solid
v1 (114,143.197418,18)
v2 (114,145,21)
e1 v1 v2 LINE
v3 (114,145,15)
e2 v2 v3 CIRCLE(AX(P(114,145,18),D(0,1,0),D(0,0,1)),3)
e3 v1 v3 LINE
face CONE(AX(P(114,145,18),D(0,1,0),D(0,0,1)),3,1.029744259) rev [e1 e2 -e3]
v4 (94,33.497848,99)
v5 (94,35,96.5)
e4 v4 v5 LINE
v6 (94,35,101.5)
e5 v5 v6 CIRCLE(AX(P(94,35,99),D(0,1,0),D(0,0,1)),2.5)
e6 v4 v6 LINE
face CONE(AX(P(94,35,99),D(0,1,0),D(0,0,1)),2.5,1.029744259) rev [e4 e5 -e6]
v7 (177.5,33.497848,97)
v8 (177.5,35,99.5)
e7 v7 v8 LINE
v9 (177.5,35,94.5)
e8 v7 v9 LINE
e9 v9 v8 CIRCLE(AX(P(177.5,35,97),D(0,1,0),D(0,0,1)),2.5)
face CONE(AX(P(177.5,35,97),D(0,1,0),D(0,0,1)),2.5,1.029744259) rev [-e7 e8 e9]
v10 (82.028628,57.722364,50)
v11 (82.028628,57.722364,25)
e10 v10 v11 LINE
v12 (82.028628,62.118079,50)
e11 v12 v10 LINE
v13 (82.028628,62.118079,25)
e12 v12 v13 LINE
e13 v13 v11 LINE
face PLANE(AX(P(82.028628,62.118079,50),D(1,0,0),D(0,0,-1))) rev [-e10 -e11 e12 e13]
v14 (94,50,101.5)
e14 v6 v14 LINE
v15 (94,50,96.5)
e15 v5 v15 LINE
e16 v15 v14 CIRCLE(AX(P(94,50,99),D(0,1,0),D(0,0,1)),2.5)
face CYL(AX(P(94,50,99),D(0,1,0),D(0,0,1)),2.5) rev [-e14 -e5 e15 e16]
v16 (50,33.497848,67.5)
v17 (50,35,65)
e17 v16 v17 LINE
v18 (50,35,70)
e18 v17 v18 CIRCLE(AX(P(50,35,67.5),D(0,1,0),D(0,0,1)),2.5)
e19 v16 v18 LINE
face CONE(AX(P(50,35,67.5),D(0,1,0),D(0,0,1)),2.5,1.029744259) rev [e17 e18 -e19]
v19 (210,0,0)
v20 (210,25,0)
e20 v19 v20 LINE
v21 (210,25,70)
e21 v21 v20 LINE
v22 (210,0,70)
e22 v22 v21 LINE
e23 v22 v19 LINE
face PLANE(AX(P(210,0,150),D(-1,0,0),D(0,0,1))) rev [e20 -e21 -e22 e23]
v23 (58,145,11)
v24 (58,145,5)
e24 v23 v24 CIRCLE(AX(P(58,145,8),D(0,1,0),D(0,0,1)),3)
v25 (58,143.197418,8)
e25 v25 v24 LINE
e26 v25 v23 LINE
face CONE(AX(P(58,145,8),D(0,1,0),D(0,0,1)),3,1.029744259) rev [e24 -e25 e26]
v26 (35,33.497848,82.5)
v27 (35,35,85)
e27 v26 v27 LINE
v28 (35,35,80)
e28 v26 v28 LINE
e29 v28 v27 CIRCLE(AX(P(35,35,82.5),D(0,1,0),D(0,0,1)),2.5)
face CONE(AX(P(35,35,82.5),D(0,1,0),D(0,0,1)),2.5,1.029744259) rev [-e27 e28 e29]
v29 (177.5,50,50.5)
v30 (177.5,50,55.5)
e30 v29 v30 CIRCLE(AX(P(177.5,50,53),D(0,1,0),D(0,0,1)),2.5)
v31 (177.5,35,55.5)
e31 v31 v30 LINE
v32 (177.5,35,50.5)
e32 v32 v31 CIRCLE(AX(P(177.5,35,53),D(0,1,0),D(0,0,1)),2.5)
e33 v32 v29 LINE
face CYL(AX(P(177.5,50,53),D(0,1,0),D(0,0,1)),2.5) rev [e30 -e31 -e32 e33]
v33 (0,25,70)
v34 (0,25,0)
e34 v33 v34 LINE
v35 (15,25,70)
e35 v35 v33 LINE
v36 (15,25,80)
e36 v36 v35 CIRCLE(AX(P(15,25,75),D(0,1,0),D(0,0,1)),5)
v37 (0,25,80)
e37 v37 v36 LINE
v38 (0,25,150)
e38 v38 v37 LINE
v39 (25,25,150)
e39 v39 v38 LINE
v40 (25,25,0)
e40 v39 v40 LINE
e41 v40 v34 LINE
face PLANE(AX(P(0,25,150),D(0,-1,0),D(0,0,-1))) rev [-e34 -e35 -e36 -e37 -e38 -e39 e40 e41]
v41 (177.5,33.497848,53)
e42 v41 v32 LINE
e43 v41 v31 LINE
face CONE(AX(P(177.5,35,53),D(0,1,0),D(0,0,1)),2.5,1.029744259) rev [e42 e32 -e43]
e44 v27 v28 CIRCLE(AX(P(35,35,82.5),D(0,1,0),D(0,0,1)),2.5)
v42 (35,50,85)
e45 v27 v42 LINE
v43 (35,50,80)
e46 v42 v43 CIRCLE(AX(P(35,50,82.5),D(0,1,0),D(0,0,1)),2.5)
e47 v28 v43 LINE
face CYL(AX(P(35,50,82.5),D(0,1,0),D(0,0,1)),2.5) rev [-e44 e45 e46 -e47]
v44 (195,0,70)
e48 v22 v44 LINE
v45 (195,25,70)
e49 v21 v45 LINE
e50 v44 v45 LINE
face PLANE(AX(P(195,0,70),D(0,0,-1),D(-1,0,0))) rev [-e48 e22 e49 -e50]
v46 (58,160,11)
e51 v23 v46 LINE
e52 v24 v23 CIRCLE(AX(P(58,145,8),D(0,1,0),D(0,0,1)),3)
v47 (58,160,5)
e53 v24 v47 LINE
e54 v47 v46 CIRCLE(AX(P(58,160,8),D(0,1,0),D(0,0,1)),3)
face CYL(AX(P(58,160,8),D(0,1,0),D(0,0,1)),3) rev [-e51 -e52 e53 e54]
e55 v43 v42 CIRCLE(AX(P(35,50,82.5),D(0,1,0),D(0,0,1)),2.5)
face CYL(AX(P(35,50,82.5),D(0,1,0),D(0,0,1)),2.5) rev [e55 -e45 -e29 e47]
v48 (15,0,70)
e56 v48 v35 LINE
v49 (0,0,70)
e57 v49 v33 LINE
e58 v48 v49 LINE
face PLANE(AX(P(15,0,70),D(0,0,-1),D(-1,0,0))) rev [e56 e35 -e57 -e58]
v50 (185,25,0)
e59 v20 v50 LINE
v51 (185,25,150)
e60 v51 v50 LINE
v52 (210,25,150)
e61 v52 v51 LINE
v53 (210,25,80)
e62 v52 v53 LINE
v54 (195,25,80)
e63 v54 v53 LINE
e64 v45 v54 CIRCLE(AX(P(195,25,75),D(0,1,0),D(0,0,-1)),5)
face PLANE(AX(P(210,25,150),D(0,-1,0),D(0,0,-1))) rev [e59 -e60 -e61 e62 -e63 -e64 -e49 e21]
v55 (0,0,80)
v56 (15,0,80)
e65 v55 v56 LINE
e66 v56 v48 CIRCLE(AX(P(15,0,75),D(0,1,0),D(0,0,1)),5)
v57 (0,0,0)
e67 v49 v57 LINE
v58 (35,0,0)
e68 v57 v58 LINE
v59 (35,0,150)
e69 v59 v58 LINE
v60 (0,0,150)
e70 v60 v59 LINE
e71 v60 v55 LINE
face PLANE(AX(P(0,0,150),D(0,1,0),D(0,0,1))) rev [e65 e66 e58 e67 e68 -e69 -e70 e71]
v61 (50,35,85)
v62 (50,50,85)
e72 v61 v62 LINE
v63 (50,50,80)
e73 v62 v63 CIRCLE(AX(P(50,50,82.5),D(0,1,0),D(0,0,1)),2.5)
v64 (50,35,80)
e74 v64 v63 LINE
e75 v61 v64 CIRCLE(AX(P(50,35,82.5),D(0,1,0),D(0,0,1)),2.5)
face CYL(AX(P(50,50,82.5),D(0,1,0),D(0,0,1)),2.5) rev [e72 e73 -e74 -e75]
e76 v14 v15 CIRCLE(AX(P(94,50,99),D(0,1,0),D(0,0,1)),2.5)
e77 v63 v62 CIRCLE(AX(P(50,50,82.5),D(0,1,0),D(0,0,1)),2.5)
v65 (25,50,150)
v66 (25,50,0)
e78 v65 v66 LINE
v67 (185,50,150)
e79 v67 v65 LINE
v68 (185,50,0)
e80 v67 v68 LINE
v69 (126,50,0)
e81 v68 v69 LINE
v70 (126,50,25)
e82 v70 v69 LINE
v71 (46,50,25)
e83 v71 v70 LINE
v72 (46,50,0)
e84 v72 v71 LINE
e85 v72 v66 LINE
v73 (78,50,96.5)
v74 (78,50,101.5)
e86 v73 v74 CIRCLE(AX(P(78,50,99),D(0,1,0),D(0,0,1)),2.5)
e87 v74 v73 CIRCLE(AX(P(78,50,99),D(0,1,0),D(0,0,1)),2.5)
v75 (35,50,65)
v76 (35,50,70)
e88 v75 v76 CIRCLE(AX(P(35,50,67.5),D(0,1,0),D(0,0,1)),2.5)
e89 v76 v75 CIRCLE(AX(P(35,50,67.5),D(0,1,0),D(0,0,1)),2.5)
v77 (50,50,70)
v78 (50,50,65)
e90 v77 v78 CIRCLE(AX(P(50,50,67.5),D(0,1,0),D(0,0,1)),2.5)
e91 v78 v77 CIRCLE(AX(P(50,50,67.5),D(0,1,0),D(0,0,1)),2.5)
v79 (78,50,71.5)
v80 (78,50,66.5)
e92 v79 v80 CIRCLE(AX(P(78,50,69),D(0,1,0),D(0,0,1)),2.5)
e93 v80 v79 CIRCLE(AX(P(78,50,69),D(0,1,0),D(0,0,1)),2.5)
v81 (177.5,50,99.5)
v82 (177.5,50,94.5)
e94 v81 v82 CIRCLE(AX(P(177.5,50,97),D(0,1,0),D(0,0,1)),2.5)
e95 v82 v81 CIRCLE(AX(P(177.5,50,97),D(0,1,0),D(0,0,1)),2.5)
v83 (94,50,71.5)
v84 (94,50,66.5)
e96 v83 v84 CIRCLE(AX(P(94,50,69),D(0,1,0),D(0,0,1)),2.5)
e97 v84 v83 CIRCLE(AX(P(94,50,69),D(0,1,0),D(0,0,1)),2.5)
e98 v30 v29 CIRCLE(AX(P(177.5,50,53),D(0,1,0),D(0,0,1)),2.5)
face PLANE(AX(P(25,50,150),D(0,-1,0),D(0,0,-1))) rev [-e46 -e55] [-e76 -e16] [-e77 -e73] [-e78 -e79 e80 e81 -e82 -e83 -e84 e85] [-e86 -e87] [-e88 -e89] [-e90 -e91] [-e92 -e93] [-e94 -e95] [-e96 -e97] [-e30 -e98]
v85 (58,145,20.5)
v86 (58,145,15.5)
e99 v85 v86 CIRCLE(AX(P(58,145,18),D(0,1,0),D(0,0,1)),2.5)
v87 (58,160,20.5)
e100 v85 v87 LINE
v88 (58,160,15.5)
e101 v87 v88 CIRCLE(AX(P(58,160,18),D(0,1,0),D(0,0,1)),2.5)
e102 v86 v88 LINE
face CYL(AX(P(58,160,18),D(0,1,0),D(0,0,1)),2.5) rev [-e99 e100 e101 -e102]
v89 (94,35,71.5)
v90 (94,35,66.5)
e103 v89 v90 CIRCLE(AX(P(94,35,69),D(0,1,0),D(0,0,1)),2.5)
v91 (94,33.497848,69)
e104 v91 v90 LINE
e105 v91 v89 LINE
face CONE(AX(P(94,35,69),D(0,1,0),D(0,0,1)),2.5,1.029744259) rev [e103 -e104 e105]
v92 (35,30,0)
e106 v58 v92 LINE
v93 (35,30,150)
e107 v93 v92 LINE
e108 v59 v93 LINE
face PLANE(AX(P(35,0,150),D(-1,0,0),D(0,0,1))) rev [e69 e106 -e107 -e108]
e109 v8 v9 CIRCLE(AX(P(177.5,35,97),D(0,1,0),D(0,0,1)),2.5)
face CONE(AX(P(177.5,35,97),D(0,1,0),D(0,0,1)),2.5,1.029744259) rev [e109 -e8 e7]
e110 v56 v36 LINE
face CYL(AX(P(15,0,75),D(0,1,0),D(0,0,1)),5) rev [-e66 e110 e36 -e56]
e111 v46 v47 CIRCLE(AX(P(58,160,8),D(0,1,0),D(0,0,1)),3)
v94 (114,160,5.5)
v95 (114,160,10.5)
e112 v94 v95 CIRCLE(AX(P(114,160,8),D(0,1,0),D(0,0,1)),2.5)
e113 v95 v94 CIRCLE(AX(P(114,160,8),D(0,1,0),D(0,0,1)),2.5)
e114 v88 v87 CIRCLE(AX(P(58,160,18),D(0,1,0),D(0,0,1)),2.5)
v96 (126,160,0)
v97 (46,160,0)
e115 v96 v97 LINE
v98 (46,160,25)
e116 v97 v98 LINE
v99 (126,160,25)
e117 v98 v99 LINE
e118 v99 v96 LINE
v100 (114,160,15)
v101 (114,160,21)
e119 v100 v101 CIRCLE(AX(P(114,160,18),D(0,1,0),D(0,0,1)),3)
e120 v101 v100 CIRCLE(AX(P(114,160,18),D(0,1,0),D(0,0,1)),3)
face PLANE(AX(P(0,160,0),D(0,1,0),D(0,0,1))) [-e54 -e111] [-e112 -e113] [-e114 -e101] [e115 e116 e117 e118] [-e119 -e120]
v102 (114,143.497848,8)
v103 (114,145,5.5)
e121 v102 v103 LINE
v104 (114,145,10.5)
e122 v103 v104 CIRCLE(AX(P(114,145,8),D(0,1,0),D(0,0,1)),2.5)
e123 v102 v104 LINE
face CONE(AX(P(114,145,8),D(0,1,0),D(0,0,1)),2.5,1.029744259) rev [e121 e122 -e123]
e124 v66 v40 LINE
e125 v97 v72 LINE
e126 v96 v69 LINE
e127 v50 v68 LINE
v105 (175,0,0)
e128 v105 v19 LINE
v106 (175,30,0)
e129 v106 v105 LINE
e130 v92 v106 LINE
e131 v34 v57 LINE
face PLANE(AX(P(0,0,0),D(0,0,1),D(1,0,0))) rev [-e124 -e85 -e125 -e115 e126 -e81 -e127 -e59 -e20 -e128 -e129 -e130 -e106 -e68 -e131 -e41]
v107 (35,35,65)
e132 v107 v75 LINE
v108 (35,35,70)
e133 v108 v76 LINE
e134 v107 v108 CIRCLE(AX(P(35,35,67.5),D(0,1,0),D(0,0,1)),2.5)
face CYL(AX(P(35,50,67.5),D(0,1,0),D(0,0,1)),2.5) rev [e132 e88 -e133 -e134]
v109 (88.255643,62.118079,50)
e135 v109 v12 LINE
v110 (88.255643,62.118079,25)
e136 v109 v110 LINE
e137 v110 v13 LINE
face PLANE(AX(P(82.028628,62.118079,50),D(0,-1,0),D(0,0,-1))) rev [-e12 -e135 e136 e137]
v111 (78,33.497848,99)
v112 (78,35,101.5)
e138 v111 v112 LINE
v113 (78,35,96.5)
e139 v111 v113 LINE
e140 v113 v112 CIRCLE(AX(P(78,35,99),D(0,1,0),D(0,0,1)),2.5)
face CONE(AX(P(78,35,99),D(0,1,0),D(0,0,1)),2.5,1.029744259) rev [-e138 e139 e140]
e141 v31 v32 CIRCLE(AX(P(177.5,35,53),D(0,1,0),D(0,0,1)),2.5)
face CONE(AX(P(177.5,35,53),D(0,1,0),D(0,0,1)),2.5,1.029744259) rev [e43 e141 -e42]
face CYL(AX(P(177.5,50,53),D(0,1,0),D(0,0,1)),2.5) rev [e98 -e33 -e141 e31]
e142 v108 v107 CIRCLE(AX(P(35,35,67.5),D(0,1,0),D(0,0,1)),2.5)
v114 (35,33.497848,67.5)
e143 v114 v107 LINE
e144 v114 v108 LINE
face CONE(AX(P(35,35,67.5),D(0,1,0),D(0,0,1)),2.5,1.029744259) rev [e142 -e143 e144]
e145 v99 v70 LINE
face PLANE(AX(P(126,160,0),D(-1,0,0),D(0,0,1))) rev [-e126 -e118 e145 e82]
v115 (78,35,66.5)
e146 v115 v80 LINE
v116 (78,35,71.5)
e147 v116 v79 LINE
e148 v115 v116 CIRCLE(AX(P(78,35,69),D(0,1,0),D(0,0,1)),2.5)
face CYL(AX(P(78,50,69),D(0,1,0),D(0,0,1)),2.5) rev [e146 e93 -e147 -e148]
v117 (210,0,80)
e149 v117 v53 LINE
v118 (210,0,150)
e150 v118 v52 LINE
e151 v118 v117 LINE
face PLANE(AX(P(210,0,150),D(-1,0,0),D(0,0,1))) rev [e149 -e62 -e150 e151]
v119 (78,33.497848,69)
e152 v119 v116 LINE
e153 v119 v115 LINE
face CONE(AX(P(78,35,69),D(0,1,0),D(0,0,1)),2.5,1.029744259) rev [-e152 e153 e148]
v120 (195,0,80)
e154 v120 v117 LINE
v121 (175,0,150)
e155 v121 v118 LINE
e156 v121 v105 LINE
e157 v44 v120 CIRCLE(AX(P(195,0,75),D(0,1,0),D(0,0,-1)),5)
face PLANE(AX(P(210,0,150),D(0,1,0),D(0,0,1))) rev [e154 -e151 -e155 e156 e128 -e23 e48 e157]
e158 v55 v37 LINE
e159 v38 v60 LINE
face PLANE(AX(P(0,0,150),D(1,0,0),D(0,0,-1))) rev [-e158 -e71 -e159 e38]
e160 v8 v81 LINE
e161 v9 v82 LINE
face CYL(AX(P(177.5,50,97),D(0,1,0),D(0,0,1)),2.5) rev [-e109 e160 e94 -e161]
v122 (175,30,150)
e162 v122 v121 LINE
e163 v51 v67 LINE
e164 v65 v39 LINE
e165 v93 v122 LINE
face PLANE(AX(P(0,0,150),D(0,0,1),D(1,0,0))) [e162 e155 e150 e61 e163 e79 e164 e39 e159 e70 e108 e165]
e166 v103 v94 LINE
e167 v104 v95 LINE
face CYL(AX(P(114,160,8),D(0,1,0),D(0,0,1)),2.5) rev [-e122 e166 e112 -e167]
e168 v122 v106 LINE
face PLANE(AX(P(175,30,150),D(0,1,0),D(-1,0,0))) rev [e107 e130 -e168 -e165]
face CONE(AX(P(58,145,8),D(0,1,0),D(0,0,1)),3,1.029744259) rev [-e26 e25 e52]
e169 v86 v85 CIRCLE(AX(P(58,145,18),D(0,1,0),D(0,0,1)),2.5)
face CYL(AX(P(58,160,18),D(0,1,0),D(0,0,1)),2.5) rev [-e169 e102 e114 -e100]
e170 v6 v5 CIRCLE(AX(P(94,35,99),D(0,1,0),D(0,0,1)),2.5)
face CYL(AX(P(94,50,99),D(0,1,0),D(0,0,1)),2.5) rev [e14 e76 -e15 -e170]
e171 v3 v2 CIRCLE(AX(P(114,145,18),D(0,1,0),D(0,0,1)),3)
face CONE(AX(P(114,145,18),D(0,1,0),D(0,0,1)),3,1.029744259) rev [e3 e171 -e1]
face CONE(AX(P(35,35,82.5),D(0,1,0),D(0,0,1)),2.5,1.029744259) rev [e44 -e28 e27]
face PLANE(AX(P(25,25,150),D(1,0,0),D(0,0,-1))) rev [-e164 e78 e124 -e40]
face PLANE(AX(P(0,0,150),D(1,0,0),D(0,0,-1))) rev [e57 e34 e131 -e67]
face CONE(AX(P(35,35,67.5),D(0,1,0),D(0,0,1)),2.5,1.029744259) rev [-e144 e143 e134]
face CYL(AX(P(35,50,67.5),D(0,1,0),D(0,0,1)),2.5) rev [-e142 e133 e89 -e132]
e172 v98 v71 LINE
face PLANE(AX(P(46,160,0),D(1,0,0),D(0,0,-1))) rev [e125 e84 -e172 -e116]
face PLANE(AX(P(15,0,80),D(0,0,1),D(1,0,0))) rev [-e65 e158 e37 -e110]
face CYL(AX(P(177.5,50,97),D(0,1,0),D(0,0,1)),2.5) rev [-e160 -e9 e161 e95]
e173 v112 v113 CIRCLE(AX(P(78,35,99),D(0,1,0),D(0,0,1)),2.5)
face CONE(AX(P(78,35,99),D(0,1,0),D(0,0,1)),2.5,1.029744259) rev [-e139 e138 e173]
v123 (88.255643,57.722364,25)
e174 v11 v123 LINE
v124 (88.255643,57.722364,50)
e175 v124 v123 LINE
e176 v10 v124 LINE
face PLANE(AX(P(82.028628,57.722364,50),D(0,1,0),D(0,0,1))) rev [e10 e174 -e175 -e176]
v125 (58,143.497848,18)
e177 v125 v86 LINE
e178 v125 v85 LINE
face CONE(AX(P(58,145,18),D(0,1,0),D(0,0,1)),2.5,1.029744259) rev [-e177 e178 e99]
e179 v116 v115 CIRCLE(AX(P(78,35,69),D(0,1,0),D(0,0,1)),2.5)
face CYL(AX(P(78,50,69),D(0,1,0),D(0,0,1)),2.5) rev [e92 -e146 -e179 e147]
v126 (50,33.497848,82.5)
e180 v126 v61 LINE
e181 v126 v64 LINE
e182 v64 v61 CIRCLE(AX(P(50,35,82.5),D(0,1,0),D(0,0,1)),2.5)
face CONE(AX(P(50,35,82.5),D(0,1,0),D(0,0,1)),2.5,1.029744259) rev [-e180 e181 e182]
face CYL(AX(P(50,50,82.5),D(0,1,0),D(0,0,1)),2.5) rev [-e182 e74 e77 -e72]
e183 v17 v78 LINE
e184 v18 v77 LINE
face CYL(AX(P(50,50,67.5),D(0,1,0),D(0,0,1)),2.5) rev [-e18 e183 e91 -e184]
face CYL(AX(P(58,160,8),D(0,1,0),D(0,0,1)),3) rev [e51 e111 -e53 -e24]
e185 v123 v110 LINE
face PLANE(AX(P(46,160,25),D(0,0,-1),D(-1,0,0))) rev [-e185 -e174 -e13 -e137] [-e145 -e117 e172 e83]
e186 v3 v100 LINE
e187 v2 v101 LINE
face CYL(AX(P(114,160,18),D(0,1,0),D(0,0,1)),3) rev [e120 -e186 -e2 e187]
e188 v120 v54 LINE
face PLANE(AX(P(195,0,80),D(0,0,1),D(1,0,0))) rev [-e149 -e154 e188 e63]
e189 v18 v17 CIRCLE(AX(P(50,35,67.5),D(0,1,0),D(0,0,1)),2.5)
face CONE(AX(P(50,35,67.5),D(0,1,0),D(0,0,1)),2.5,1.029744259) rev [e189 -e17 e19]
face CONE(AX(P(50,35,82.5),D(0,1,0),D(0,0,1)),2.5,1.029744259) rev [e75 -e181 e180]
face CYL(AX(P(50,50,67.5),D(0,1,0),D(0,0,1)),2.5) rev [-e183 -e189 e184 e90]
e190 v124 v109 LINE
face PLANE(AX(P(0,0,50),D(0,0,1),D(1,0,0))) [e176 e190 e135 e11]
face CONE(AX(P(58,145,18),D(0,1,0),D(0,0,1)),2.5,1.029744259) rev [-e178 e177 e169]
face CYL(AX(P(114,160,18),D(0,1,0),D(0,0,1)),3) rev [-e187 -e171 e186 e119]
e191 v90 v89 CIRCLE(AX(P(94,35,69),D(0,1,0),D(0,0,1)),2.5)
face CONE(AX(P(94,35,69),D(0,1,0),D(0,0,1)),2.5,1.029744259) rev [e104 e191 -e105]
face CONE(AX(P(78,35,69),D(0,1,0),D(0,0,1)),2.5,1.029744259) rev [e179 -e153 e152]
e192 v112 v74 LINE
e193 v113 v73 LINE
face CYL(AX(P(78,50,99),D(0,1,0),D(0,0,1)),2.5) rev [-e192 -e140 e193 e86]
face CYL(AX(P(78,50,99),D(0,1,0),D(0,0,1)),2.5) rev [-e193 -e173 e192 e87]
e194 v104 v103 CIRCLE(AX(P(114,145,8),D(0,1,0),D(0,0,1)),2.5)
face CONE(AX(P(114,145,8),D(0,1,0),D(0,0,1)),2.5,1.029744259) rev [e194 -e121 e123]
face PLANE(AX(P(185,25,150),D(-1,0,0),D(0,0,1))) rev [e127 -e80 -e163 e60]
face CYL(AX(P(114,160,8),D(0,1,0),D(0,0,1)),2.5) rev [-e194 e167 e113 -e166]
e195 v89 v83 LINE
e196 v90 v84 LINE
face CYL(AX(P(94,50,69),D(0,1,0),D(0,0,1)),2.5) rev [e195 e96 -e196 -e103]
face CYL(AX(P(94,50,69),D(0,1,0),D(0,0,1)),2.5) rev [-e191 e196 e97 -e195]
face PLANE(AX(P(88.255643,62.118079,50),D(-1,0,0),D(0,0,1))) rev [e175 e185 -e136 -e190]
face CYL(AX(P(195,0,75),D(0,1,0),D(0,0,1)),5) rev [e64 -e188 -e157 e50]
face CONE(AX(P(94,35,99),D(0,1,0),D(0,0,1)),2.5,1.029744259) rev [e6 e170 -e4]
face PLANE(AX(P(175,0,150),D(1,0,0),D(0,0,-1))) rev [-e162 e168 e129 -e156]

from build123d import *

# Parameters (mm, degrees)
BOSS_EXTRUDE1_DEPTH        = 150
CUT_EXTRUDE1_DEPTH         = 260.277843249
M6_TAPPED_HOLE1_D          = 5
M6_TAPPED_HOLE1_DEPTH      = 15
M6_TAPPED_HOLE1_TIP        = 1.502151548
SKETCH13_W                 = 80
SKETCH13_H                 = 25
BOSS_EXTRUDE2_DEPTH        = 110
M6_TAPPED_HOLE2_D          = 5
M6_TAPPED_HOLE2_DEPTH      = 15
M6_TAPPED_HOLE2_TIP        = 1.502151548
F_6_0MM_DOWEL_HOLE_1_D     = 6
F_6_0MM_DOWEL_HOLE_1_DEPTH = 15
F_6_0MM_DOWEL_HOLE_1_TIP   = 1.802581857
SKETCH20_W                 = 6.227014718
SKETCH20_H                 = 4.395715082
BOSS_EXTRUDE3_DEPTH        = 25


with BuildPart() as part:
    # Sketch1 → Boss-Extrude1 (new body)
    with BuildSketch(Plane.XY):
        Polygon((0, 0), (0, 25), (25, 25), (25, 50), (185, 50), (185, 25), (210, 25), (210, 0), (175, 0), (175, 30), (35, 30), (35, 0), align=None)
    extrude(amount=BOSS_EXTRUDE1_DEPTH)

    # Sketch9 → Cut-Extrude1 (cut, through all)
    with BuildSketch(Plane(origin=(0, 25, 0), x_dir=(1, 0, 0), z_dir=(0, 1, 0))):
        with BuildLine():
            Line((210, -70), (210, -80))
            Line((210, -80), (195, -80))
            ThreePointArc((195, -80), (190, -75), (195, -70))
            Line((195, -70), (210, -70))
        make_face()
        with BuildLine():
            Line((15, -70), (0, -70))
            Line((0, -70), (0, -80))
            Line((0, -80), (15, -80))
            ThreePointArc((15, -80), (20, -75), (15, -70))
        make_face()
    extrude(amount=-CUT_EXTRUDE1_DEPTH, mode=Mode.SUBTRACT)

    # M6 Tapped Hole1
    with Locations(Plane(origin=(0, 50, 0), x_dir=(1, 0, 0), z_dir=(0, 1, 0))):
        with Locations((35, -82.5), (35, -67.5), (50, -67.5), (50, -82.5), (78, -69), (78, -99), (94, -69), (94, -99), (177.5, -97), (177.5, -53)):
            Hole(M6_TAPPED_HOLE1_D / 2, depth=M6_TAPPED_HOLE1_DEPTH)
            with Locations((0, 0, -(M6_TAPPED_HOLE1_DEPTH + M6_TAPPED_HOLE1_TIP / 2))):  # 118° drill point
                Cone(0, M6_TAPPED_HOLE1_D / 2, M6_TAPPED_HOLE1_TIP, mode=Mode.SUBTRACT)

    # Sketch13 → Boss-Extrude2 (add)
    with BuildSketch(Plane(origin=(0, 50, 0), x_dir=(1, 0, 0), z_dir=(0, 1, 0))):
        with Locations((86, -12.5)):
            Rectangle(SKETCH13_W, SKETCH13_H)
    extrude(amount=BOSS_EXTRUDE2_DEPTH)

    # M6 Tapped Hole2
    with Locations(Plane(origin=(0, 160, 0), x_dir=(1, 0, 0), z_dir=(0, 1, 0))):
        with Locations((58, -18), (114, -8)):
            Hole(M6_TAPPED_HOLE2_D / 2, depth=M6_TAPPED_HOLE2_DEPTH)
            with Locations((0, 0, -(M6_TAPPED_HOLE2_DEPTH + M6_TAPPED_HOLE2_TIP / 2))):  # 118° drill point
                Cone(0, M6_TAPPED_HOLE2_D / 2, M6_TAPPED_HOLE2_TIP, mode=Mode.SUBTRACT)

    # Ø6.0mm dowel hole 1
    with Locations(Plane(origin=(0, 160, 0), x_dir=(1, 0, 0), z_dir=(0, 1, 0))):
        with Locations((58, -8), (114, -18)):
            Hole(F_6_0MM_DOWEL_HOLE_1_D / 2, depth=F_6_0MM_DOWEL_HOLE_1_DEPTH)
            with Locations((0, 0, -(F_6_0MM_DOWEL_HOLE_1_DEPTH + F_6_0MM_DOWEL_HOLE_1_TIP / 2))):  # 118° drill point
                Cone(0, F_6_0MM_DOWEL_HOLE_1_D / 2, F_6_0MM_DOWEL_HOLE_1_TIP, mode=Mode.SUBTRACT)

    # Sketch20 → Boss-Extrude3 (add)
    with BuildSketch(Plane.XY.offset(25)):
        with Locations((85.142135624, 59.920221849)):
            Rectangle(SKETCH20_W, SKETCH20_H)
    extrude(amount=BOSS_EXTRUDE3_DEPTH)


solid = part.part
